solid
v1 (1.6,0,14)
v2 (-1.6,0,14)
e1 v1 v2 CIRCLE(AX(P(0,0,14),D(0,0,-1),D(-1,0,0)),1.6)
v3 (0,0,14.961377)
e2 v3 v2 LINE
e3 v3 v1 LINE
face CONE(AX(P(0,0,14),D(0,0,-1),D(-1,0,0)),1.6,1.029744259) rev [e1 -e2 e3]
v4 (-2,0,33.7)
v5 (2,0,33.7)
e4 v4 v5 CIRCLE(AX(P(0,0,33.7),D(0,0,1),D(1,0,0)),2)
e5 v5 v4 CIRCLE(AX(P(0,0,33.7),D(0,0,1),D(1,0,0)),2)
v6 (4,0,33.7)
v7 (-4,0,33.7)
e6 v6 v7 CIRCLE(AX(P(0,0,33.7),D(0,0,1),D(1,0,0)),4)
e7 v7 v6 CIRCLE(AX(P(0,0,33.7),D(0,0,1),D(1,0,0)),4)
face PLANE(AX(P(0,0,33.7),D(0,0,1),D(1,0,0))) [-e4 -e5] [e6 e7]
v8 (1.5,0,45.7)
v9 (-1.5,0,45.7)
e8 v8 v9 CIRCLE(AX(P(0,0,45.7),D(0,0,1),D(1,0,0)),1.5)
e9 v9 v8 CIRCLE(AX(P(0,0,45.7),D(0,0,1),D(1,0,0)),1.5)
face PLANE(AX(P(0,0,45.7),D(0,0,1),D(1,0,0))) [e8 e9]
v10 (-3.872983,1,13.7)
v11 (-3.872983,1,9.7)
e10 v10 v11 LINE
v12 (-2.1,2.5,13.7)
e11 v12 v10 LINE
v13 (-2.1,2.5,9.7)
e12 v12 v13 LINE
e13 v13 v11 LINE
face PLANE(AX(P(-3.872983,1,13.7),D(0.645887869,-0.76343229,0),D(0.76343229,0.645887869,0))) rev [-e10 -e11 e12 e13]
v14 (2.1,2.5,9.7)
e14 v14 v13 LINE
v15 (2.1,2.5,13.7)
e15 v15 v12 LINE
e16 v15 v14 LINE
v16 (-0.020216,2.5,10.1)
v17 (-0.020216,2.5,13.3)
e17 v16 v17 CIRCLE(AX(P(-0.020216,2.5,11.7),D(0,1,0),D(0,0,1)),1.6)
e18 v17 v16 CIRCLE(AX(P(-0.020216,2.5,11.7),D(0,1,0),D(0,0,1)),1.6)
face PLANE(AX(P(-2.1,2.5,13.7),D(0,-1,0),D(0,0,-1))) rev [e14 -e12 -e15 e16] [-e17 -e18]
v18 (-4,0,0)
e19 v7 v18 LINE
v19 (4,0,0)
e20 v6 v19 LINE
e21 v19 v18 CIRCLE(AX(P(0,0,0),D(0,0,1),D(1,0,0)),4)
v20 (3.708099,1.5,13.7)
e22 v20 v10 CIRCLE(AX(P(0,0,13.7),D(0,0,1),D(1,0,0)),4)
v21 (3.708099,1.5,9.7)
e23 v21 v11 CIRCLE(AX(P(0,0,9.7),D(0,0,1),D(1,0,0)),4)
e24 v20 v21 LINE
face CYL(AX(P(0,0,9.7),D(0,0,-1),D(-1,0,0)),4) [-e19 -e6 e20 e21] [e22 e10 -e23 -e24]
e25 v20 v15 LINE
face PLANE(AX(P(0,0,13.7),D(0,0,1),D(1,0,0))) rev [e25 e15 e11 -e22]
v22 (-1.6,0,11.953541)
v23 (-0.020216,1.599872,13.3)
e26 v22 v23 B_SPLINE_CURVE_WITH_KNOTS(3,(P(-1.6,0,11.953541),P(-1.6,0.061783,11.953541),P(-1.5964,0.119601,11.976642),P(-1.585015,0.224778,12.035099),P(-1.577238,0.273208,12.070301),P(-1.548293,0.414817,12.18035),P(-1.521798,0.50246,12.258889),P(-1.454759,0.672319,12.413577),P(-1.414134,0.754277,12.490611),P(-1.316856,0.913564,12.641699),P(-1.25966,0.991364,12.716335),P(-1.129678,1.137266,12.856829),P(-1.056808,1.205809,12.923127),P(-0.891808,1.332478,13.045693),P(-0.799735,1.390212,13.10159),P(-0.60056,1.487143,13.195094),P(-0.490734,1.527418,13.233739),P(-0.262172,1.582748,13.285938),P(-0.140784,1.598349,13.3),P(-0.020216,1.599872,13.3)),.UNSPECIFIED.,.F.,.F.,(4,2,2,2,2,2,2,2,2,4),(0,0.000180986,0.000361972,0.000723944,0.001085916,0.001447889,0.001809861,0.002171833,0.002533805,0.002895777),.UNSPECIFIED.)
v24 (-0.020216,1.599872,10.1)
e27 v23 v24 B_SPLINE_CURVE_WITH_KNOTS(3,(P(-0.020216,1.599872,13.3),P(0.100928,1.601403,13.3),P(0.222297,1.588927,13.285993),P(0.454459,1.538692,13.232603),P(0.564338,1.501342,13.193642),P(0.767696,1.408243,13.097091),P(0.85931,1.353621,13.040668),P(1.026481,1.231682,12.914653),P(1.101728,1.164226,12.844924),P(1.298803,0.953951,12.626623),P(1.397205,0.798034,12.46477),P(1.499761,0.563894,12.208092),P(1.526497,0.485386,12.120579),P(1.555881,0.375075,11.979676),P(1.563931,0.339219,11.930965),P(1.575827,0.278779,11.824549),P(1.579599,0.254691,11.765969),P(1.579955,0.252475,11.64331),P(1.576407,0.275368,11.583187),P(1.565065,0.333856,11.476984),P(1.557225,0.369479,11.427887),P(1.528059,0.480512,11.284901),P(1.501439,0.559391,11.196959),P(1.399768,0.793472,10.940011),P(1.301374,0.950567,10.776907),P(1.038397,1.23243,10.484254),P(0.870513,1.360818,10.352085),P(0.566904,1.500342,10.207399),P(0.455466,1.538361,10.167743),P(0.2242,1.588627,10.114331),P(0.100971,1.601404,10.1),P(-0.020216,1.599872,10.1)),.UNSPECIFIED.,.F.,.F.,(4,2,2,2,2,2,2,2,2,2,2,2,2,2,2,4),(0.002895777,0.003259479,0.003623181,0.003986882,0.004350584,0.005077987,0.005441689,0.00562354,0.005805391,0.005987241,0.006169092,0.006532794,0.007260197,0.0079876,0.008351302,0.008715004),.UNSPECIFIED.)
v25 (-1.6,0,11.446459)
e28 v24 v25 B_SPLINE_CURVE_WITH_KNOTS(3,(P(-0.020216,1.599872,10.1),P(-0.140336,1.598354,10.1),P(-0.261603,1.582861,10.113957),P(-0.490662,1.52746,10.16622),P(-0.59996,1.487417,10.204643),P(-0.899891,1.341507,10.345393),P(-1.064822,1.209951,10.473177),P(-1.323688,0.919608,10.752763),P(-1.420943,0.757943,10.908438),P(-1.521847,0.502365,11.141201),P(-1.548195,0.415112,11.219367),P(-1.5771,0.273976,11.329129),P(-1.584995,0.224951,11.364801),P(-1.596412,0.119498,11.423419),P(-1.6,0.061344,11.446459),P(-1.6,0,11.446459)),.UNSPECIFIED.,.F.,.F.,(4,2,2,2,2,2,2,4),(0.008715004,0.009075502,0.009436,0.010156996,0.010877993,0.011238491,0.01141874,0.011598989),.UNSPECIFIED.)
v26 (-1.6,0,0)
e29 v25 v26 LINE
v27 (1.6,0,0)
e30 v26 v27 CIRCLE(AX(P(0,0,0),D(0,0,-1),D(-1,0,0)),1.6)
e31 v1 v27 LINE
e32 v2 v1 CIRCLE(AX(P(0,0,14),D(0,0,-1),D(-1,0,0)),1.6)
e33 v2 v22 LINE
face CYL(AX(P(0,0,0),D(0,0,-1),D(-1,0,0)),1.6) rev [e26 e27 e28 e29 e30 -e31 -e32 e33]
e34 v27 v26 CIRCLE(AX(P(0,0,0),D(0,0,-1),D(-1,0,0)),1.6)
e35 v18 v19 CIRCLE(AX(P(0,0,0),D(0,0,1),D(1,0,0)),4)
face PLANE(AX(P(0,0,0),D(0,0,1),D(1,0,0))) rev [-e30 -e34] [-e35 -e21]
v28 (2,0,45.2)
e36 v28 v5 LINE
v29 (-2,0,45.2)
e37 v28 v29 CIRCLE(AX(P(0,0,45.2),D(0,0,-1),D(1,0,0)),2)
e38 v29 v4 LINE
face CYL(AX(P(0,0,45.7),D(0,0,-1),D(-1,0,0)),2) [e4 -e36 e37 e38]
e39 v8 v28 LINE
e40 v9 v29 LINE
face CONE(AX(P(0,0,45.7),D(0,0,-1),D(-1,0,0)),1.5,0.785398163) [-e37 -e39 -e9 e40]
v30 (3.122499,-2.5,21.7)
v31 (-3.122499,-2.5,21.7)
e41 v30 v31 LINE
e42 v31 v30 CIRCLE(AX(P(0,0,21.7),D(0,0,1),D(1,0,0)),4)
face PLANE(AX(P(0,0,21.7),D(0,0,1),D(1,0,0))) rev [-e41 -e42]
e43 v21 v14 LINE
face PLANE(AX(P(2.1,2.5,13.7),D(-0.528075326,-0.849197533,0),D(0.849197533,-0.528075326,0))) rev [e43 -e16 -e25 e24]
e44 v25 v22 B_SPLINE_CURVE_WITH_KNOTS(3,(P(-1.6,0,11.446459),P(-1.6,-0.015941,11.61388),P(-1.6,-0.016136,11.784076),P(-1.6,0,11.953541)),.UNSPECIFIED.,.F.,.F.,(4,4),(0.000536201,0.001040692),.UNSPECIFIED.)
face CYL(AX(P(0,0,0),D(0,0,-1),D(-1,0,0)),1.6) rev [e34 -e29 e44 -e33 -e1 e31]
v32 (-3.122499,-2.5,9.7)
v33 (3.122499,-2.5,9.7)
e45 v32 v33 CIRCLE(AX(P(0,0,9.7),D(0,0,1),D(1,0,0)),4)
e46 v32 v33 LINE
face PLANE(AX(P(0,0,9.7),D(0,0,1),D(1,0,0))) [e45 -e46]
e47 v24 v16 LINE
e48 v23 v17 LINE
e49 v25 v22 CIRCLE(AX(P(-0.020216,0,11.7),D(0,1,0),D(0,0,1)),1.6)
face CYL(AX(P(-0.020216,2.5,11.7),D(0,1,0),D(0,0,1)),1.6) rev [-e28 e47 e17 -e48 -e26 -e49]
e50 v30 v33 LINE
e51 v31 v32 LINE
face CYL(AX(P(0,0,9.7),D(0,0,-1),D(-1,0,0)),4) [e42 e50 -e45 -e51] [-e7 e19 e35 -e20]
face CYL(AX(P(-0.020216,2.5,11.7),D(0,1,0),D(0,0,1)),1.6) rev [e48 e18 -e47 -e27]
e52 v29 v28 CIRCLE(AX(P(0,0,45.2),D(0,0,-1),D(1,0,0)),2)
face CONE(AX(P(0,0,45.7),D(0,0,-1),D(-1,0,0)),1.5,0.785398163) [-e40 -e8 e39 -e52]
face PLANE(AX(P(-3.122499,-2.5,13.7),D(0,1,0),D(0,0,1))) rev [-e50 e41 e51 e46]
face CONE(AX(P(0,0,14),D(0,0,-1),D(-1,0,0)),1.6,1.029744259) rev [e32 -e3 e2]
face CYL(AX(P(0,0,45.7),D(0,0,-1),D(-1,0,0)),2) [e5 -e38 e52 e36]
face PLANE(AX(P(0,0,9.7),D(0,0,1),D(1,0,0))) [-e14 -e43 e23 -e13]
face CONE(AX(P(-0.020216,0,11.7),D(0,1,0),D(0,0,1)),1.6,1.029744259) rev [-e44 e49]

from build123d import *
from build123d.topology import SkipClean

# Parameters (mm, degrees)
SKETCH_1_2_R                   = 4
BOSS_EXTRUDE1_DEPTH            = 9.7
BOSS_EXTRUDE2_DEPTH            = 4
BOSS_EXTRUDE3_START            = 13.7
SKETCH_1_2_2_R                 = 4
BOSS_EXTRUDE3_DEPTH            = 20
SKETCH3_R                      = 2
BOSS_EXTRUDE4_DEPTH            = 12
CHAMFER1_SIZE                  = 0.5
CUT_EXTRUDE1_DEPTH             = 12
F_3_2_3_2_DIAMETER_HOLE1_D     = 3.2
F_3_2_3_2_DIAMETER_HOLE1_DEPTH = 14
F_3_2_3_2_DIAMETER_HOLE1_TIP   = 0.96137699
F_3_2_3_2_DIAMETER_HOLE2_D     = 3.2
F_3_2_3_2_DIAMETER_HOLE2_DEPTH = 2.499
F_3_2_3_2_DIAMETER_HOLE2_TIP   = 0.96137699


with BuildPart() as part:
    # Sketch 1_2 → Boss-Extrude1 (new body)
    with BuildSketch(Plane.XY):
        Circle(SKETCH_1_2_R)
    extrude(amount=BOSS_EXTRUDE1_DEPTH)

    # Sketch2 → Boss-Extrude2 (add)
    with SkipClean():  # the faces are left unmerged after this step: merging them gives an invalid solid
        with BuildSketch(Plane.XY.offset(9.7)):
            with BuildLine():
                Line((-3.872983346, 1), (-2.1, 2.5))
                Line((-2.1, 2.5), (2.1, 2.5))
                Line((2.1, 2.5), (3.708099244, 1.5))
                ThreePointArc((3.708099244, 1.5), (3.957811022, -0.579423775), (3.122498999, -2.5))
                Line((3.122498999, -2.5), (-3.122498999, -2.5))
                ThreePointArc((-3.122498999, -2.5), (-3.911098735, -0.838633823), (-3.872983346, 1))
            make_face()
        extrude(amount=BOSS_EXTRUDE2_DEPTH)

    # Sketch 1_2 2 → Boss-Extrude3 (add)
    with SkipClean():  # the faces are left unmerged after this step: merging them gives an invalid solid
        with BuildSketch(Plane.XY.offset(BOSS_EXTRUDE3_START)):
            Circle(SKETCH_1_2_2_R)
        extrude(amount=BOSS_EXTRUDE3_DEPTH)

    # Sketch3 → Boss-Extrude4 (add)
    with SkipClean():  # the faces are left unmerged after this step: merging them gives an invalid solid
        with BuildSketch(Plane.XY.offset(33.7)):
            Circle(SKETCH3_R)
        extrude(amount=BOSS_EXTRUDE4_DEPTH)

    # Chamfer1
    chamfer1_edges = [part.edges().sort_by_distance(p)[0] for p in [
        (-2, 0, 45.7),
    ]]
    chamfer(chamfer1_edges, length=CHAMFER1_SIZE)

    # Sketch4 → Cut-Extrude1 (cut)
    with SkipClean():  # the faces are left unmerged after this step: merging them gives an invalid solid
        with BuildSketch(Plane.XY.offset(9.7)):
            with BuildLine():
                Line((3.122498999, -2.5), (-3.122498999, -2.5))
                ThreePointArc((-3.122498999, -2.5), (0, -4), (3.122498999, -2.5))
            make_face()
        extrude(amount=CUT_EXTRUDE1_DEPTH, mode=Mode.SUBTRACT)

    # Ø3.2 (3.2) Diameter Hole1
    with Locations(Plane(origin=(0, 0, 0), x_dir=(-1, 0, 0), z_dir=(0, 0, -1))):
        with Locations((0, 0)):
            Hole(F_3_2_3_2_DIAMETER_HOLE1_D / 2, depth=F_3_2_3_2_DIAMETER_HOLE1_DEPTH)
            with Locations((0, 0, -(F_3_2_3_2_DIAMETER_HOLE1_DEPTH + F_3_2_3_2_DIAMETER_HOLE1_TIP / 2))):  # 118° drill point
                Cone(0, F_3_2_3_2_DIAMETER_HOLE1_D / 2, F_3_2_3_2_DIAMETER_HOLE1_TIP, mode=Mode.SUBTRACT)

    # Ø3.2 (3.2) Diameter Hole2
    with Locations(Plane(origin=(-0.020216214, 2.5, 11.7), x_dir=(0, 0, 1), z_dir=(0, 1, 0))):
        with Locations((0, 0)):
            Hole(F_3_2_3_2_DIAMETER_HOLE2_D / 2, depth=F_3_2_3_2_DIAMETER_HOLE2_DEPTH)
            with Locations((0, 0, -(F_3_2_3_2_DIAMETER_HOLE2_DEPTH + F_3_2_3_2_DIAMETER_HOLE2_TIP / 2))):  # 118° drill point
                Cone(0, F_3_2_3_2_DIAMETER_HOLE2_D / 2, F_3_2_3_2_DIAMETER_HOLE2_TIP, mode=Mode.SUBTRACT)


solid = part.part
